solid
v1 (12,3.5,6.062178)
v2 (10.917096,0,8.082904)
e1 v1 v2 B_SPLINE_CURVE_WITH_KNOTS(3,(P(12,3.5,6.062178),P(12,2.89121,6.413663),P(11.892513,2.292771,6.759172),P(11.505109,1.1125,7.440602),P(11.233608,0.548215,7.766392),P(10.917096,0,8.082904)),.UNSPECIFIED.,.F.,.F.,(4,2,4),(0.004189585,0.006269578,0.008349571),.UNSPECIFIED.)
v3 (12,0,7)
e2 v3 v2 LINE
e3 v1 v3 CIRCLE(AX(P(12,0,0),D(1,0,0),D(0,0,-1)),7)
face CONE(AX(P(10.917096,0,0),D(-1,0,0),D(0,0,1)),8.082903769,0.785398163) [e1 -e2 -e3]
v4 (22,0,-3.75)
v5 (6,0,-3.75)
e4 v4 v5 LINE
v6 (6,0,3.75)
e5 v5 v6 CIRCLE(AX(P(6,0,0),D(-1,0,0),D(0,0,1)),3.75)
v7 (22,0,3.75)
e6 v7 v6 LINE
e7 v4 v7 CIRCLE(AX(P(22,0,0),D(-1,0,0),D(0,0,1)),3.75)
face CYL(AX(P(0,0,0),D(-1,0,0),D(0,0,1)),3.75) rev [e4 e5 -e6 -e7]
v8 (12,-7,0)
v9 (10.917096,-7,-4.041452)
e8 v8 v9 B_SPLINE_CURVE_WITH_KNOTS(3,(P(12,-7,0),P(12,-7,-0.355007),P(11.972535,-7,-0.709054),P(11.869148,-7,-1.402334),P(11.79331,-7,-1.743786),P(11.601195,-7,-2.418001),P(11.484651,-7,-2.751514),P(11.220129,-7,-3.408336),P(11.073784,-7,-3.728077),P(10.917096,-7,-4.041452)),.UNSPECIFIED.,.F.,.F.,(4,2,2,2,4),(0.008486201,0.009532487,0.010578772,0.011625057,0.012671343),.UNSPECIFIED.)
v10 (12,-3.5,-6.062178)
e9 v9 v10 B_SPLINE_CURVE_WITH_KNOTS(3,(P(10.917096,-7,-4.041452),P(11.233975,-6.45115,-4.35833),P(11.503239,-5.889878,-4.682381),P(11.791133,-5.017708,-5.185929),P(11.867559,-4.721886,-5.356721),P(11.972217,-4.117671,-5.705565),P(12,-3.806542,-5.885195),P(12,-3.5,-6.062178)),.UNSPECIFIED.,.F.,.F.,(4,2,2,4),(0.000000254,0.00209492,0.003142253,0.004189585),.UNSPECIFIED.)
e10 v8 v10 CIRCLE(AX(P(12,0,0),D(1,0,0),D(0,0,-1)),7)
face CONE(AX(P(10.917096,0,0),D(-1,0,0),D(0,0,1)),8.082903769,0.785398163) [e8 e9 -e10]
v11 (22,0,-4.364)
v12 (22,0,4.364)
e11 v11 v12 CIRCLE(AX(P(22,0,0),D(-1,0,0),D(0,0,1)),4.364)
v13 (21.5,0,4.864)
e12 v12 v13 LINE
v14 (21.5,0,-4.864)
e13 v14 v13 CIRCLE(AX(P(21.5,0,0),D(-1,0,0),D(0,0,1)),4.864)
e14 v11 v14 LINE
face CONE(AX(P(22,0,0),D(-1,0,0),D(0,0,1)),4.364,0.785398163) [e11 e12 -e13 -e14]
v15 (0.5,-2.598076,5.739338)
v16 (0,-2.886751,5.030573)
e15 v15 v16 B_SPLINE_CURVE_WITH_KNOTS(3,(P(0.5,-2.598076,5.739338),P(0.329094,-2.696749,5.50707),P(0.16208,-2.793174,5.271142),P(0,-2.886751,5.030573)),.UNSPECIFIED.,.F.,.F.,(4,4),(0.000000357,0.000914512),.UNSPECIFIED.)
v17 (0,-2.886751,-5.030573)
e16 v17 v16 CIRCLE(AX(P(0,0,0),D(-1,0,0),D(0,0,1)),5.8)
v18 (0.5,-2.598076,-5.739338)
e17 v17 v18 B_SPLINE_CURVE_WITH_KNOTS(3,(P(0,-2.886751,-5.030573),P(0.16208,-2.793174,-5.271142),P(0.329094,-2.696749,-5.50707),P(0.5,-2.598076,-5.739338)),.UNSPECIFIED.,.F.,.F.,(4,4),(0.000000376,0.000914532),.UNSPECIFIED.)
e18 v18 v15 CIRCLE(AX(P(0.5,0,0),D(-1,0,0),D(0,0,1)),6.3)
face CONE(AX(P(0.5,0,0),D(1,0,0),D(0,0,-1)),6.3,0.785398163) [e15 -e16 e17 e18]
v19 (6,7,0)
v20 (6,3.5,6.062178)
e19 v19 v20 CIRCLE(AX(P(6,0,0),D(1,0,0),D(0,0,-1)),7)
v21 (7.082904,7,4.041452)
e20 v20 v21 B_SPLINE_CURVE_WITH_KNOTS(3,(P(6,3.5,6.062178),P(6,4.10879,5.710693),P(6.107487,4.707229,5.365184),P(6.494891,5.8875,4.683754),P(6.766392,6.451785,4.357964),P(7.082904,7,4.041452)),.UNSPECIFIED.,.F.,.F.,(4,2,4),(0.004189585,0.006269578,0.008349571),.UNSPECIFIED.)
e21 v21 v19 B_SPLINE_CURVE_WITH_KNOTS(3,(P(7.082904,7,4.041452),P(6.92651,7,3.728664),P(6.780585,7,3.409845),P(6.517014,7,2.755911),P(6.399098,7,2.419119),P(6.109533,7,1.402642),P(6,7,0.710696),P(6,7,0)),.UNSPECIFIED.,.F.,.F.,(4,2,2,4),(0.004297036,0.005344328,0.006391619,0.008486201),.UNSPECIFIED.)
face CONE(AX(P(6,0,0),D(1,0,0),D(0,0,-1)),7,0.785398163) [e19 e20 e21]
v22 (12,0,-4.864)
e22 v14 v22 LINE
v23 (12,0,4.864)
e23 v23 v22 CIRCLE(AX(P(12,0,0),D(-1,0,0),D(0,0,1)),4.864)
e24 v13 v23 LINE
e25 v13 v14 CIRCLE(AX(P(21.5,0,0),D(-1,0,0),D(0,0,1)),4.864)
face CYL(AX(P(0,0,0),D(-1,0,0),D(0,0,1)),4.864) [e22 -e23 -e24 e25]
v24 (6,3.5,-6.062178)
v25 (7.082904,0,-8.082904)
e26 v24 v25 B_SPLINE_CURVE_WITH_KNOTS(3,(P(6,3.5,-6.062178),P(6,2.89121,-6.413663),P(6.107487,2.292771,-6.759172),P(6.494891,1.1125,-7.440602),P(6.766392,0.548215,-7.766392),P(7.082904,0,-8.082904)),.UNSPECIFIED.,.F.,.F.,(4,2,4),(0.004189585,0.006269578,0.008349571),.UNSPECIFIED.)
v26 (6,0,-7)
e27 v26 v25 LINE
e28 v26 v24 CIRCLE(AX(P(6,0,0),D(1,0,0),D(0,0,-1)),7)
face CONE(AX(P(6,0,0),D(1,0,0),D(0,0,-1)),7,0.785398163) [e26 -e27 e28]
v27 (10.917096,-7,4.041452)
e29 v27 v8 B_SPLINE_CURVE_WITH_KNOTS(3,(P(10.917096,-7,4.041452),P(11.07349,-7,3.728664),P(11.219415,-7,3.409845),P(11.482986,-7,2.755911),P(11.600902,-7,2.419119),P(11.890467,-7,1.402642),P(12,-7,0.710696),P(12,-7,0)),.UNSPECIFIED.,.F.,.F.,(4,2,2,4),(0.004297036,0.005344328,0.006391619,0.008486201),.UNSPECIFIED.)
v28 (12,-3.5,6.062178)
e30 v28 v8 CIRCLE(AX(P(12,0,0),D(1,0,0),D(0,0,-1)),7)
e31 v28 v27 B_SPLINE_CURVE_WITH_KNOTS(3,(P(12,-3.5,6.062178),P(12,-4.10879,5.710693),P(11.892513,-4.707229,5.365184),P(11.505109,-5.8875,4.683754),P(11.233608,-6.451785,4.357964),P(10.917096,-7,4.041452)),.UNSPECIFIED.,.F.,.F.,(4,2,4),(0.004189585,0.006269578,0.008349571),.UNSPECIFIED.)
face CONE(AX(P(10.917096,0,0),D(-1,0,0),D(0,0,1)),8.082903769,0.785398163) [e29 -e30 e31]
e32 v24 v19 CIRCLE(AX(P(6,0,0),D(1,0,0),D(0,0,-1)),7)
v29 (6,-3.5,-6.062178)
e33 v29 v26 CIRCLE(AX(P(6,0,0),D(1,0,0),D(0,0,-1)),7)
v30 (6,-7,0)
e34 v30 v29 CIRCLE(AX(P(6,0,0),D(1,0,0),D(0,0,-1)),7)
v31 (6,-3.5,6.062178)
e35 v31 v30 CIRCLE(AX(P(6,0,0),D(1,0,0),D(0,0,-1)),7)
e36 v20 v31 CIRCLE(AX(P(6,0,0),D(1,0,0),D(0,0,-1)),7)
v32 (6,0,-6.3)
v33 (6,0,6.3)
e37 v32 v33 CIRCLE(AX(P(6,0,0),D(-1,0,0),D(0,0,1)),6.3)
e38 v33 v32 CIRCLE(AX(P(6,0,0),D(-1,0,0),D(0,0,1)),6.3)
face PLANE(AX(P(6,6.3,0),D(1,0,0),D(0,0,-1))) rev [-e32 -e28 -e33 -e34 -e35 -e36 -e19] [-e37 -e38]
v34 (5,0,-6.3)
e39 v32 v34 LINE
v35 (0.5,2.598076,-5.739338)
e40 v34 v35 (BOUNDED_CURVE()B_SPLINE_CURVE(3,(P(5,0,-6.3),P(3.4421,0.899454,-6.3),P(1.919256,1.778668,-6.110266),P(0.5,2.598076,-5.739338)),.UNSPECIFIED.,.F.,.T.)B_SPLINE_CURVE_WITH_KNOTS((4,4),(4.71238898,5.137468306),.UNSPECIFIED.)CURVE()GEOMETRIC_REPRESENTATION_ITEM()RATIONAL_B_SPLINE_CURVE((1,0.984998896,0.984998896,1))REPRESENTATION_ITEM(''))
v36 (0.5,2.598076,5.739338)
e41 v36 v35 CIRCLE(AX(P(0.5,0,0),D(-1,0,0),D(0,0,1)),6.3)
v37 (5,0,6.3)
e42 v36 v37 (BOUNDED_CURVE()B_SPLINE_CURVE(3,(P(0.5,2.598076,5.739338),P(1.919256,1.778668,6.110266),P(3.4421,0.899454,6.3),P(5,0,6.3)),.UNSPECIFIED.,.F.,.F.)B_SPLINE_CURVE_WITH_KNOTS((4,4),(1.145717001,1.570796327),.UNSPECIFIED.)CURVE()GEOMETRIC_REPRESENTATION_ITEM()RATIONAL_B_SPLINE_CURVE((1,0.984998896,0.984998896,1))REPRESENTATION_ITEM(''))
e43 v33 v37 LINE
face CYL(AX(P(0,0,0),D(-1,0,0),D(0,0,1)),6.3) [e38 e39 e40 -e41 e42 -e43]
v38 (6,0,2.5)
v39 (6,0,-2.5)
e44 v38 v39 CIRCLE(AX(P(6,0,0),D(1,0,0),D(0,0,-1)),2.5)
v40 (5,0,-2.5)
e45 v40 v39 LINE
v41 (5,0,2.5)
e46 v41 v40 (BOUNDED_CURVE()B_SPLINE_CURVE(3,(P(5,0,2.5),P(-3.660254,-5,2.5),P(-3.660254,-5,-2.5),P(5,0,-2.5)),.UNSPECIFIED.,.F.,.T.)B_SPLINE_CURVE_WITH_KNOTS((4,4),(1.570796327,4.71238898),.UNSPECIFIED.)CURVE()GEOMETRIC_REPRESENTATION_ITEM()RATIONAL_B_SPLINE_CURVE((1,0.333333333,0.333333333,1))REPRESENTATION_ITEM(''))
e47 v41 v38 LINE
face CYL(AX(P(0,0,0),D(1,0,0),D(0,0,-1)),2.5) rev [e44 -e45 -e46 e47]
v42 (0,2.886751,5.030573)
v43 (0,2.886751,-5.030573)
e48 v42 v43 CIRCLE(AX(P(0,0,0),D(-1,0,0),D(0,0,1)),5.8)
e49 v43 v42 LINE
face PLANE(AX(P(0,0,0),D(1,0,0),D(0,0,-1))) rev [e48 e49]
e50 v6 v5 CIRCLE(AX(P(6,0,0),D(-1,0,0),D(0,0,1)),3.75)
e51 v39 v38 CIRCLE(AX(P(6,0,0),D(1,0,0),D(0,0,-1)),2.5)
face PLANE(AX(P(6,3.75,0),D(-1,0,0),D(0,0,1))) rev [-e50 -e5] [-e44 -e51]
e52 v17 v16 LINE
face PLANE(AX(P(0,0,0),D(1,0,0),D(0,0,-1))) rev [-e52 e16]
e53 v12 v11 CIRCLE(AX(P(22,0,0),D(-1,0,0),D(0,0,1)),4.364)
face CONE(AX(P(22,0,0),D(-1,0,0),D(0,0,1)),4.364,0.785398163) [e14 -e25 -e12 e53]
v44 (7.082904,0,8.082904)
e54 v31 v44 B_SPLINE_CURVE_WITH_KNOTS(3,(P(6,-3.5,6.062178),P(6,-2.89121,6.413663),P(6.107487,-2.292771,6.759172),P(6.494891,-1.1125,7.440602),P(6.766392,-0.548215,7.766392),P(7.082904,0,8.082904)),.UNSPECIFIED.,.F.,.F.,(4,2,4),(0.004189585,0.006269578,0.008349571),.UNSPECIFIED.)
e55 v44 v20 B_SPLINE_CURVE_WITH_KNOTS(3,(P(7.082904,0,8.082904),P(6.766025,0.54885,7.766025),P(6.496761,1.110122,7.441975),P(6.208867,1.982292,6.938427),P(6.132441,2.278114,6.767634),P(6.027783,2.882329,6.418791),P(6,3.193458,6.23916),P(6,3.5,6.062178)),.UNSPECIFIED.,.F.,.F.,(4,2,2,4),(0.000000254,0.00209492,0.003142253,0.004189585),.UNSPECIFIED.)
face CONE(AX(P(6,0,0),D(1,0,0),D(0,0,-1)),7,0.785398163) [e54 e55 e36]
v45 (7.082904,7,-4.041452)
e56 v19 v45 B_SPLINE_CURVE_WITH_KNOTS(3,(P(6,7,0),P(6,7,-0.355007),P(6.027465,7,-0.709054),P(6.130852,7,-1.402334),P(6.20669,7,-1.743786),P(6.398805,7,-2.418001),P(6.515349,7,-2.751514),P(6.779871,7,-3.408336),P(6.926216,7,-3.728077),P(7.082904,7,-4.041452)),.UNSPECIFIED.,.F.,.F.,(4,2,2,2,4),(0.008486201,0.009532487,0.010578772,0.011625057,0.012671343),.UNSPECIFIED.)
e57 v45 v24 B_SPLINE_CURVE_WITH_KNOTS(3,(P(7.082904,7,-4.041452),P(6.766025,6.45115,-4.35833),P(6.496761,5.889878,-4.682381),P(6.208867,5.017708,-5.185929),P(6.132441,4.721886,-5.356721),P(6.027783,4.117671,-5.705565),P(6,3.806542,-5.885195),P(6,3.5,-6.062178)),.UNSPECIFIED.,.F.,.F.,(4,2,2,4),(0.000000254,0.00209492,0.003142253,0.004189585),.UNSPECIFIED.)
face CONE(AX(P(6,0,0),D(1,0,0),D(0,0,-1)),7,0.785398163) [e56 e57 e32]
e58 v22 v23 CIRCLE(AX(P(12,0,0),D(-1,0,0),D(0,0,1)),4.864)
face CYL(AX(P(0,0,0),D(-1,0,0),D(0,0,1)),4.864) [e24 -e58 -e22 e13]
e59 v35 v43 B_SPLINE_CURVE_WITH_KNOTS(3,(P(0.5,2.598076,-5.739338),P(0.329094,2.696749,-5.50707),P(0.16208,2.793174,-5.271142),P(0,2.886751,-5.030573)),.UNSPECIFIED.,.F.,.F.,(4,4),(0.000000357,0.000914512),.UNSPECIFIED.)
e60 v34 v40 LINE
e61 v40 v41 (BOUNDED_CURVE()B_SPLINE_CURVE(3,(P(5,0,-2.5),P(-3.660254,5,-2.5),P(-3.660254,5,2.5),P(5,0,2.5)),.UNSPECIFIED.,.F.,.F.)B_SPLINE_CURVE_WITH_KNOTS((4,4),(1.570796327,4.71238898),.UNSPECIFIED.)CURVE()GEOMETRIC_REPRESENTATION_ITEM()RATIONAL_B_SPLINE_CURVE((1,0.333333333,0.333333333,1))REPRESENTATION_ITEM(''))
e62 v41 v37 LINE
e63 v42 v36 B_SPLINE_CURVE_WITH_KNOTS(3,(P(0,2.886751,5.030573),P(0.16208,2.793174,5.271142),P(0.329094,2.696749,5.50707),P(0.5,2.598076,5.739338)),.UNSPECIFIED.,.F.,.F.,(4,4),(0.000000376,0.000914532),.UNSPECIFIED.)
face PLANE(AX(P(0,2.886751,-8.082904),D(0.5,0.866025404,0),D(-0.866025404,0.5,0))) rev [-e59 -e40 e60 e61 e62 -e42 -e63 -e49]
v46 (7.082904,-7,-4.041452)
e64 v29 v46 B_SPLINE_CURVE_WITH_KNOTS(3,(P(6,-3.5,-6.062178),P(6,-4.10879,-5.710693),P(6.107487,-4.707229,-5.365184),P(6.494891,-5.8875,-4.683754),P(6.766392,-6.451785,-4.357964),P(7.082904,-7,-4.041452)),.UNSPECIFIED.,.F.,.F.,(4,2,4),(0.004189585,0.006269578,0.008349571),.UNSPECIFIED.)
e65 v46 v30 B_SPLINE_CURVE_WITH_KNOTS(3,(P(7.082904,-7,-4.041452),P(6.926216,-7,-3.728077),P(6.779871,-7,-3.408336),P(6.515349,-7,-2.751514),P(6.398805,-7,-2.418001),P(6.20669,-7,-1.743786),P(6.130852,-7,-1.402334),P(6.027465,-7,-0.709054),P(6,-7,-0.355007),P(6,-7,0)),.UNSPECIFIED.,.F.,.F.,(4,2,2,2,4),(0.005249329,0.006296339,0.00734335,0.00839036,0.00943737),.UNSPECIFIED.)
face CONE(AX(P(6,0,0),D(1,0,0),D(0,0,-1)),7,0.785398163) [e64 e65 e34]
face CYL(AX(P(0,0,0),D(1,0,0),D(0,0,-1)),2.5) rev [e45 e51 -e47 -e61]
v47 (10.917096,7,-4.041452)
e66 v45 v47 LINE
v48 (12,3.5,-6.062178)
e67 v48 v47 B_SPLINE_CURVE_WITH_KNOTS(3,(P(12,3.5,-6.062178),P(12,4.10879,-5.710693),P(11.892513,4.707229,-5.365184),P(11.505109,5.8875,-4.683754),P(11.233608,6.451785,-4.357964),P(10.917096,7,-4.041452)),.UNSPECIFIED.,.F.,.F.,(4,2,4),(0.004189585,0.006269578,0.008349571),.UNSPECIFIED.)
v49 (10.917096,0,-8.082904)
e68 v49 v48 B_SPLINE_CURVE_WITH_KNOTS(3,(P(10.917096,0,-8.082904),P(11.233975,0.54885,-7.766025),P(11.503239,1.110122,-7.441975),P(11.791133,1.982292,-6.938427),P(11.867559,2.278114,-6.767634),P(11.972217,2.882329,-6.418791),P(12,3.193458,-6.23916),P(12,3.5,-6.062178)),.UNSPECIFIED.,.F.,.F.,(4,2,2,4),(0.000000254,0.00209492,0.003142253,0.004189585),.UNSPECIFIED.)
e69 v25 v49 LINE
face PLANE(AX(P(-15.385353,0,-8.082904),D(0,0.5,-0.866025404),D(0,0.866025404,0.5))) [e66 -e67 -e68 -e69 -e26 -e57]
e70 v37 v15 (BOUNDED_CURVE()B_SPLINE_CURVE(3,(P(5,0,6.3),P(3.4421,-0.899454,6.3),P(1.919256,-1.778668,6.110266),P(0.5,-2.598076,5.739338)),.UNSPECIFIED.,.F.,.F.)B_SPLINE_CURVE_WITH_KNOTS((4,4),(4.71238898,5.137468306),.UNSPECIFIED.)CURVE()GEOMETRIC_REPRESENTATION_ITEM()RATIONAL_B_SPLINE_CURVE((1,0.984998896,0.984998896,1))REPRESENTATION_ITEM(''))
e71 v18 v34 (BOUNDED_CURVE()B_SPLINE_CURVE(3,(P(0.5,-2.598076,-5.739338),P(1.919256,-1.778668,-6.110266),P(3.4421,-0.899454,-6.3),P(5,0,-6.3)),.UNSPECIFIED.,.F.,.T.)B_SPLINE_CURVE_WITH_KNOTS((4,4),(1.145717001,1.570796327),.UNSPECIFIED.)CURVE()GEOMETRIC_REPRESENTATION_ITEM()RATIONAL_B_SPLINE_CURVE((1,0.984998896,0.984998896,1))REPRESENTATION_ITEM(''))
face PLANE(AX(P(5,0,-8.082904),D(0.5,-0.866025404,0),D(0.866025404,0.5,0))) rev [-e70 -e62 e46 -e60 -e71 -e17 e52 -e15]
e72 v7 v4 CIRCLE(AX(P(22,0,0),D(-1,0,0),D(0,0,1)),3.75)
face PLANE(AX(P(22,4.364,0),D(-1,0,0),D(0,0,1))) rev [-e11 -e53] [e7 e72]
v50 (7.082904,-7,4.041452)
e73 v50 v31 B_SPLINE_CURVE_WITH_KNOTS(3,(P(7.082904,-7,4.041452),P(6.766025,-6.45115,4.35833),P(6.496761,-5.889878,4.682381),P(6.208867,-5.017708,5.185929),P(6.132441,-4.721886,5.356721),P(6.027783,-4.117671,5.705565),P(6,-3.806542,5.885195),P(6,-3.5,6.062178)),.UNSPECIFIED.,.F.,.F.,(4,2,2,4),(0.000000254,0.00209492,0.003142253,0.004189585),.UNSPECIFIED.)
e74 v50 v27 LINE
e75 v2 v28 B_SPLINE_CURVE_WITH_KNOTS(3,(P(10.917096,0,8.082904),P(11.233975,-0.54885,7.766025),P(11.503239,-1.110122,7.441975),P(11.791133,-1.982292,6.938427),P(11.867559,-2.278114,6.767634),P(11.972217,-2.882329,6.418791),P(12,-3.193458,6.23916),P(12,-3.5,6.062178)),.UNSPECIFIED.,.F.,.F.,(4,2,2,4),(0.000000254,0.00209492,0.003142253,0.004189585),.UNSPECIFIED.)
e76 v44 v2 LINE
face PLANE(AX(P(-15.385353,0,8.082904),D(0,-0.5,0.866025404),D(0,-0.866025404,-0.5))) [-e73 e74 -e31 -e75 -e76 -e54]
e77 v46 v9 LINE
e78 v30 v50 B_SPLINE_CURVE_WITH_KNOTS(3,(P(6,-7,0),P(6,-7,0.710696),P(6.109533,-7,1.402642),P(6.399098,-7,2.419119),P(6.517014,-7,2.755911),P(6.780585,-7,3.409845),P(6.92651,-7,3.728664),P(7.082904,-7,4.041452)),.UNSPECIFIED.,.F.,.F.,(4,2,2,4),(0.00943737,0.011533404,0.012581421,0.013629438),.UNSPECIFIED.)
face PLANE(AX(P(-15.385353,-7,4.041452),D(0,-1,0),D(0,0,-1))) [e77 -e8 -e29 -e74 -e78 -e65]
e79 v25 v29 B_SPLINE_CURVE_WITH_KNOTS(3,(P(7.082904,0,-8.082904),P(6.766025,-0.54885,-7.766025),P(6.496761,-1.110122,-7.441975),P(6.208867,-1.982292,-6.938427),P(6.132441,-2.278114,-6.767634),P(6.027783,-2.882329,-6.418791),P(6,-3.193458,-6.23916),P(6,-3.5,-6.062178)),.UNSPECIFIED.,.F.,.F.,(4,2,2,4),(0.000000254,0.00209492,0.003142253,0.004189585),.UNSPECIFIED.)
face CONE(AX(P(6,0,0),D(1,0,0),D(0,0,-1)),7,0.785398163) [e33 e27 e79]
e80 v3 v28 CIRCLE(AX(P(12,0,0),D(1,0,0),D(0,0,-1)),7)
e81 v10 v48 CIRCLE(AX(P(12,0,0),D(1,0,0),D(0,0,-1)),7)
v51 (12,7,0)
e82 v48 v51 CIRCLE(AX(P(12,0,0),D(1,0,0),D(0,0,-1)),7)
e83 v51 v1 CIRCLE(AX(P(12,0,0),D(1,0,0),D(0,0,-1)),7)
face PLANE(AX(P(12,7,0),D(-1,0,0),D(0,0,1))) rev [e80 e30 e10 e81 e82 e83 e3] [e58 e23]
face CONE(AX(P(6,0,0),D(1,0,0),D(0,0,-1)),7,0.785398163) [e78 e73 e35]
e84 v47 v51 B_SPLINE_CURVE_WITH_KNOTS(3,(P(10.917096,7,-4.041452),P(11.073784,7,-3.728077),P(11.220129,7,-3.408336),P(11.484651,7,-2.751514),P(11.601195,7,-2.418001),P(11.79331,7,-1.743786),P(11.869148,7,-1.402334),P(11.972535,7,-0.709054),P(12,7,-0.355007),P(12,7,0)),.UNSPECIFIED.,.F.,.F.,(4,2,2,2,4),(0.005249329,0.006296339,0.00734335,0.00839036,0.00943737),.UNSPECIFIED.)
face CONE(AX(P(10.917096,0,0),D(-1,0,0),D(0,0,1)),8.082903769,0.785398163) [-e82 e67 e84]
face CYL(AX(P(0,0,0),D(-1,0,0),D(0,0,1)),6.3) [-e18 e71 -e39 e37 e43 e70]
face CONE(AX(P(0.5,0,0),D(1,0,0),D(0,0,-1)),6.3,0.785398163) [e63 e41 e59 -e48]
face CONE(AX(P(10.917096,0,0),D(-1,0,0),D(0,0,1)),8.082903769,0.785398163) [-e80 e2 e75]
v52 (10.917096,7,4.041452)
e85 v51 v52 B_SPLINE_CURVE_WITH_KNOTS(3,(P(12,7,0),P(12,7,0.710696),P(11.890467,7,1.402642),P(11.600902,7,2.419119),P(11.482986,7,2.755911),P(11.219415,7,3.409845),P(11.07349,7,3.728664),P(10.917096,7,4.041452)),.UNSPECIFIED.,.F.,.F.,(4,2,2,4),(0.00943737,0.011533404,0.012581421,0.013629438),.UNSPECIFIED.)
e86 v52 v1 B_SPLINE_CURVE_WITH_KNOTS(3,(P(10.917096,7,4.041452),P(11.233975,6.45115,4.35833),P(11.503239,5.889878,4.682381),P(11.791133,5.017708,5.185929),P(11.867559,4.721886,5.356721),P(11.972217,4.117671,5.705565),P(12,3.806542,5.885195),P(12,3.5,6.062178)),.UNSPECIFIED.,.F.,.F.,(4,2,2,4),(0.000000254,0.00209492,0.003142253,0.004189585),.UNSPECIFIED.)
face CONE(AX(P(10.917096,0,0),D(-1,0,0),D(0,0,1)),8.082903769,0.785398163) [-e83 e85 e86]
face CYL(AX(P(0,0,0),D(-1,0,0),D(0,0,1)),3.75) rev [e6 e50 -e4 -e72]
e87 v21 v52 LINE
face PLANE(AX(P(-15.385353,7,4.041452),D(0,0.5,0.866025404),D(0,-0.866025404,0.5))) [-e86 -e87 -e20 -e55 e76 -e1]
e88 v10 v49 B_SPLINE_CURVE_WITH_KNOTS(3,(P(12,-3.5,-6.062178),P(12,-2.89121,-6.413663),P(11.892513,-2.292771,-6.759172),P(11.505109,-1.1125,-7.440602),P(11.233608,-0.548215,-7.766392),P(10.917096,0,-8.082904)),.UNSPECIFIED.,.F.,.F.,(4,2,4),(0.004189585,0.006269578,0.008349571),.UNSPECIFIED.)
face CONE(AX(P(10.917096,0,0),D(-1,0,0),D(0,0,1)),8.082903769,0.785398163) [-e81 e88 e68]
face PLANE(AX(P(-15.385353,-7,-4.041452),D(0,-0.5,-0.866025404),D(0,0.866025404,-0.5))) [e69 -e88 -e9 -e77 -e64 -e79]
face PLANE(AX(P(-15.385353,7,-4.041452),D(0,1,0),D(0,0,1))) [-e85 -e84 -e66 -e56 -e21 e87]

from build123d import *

# Parameters (mm, degrees)
SKETCH2_R               = 4.864
BOSS_EXTRUDE1_DEPTH     = 6
CUT_EXTRUDE1_DEPTH      = 25.460853079
CUT_EXTRUDE1_DEPTH_BACK = 25.460853079
SKETCH5_R               = 2.5
CUT_EXTRUDE2_DEPTH      = 20.244046698


with BuildPart() as part:
    # Sketch1 → Revolve1 (revolve)
    with BuildSketch(Plane.XY, mode=Mode.PRIVATE) as revolve1_sk:
        Polygon((0, 0), (0, 5.8), (0.5, 6.3), (6, 6.3), (6, 7), (12, 7), (12, 4.864), (21.5, 4.864), (22, 4.364), (22, 3.75), (6, 3.75), (6, 0), align=None)
    revolve(revolve1_sk.sketch.rotate(Axis((0, 0, 0), (1, 0, 0)), 90), axis=Axis((0, 0, 0), (1, 0, 0)))

    # Sketch2 → Boss-Extrude1 (add)
    with BuildSketch(Plane(origin=(12, 0, 0), x_dir=(0, 0, -1), z_dir=(1, 0, 0))):
        Polygon((8.082903769, 0), (4.041451884, 7), (-4.041451884, 7), (-8.082903769, 0), (-4.041451884, -7), (4.041451884, -7), align=None)
        with Locations(Location((0, 0, 0), (0, 0, 180))):
            Circle(SKETCH2_R, mode=Mode.SUBTRACT)
    extrude(amount=-BOSS_EXTRUDE1_DEPTH)

    # Sketch3 → Cut-Revolve1 (revolve, cut)
    with BuildSketch(Plane(origin=(0, 0, 0), x_dir=(1, 0, 0), z_dir=(0, 1, 0))):
        Polygon((10.917096231, 8.082903769), (12, 7), (12, 8.082903769), align=None)
        Polygon((6, 7), (7.082903769, 8.082903769), (6, 8.082903769), align=None)
    revolve(axis=Axis((0, 0, 0), (-1, 0, 0)), mode=Mode.SUBTRACT)

    # Sketch4 → Cut-Extrude1 (cut, two sides: drawn at the far end of the back side and taken through both)
    with BuildSketch(Plane.XY.offset(-CUT_EXTRUDE1_DEPTH_BACK)):
        Polygon((0, 2.886751346), (5, 0), (0, -2.886751346), align=None)
    extrude(amount=CUT_EXTRUDE1_DEPTH + CUT_EXTRUDE1_DEPTH_BACK, mode=Mode.SUBTRACT)

    # Sketch5 → Cut-Extrude2 (cut, through all)
    with BuildSketch(Plane(origin=(6, 0, 0), x_dir=(0, 0, -1), z_dir=(1, 0, 0))):
        Circle(SKETCH5_R)
    extrude(amount=-CUT_EXTRUDE2_DEPTH, mode=Mode.SUBTRACT)


solid = part.part
